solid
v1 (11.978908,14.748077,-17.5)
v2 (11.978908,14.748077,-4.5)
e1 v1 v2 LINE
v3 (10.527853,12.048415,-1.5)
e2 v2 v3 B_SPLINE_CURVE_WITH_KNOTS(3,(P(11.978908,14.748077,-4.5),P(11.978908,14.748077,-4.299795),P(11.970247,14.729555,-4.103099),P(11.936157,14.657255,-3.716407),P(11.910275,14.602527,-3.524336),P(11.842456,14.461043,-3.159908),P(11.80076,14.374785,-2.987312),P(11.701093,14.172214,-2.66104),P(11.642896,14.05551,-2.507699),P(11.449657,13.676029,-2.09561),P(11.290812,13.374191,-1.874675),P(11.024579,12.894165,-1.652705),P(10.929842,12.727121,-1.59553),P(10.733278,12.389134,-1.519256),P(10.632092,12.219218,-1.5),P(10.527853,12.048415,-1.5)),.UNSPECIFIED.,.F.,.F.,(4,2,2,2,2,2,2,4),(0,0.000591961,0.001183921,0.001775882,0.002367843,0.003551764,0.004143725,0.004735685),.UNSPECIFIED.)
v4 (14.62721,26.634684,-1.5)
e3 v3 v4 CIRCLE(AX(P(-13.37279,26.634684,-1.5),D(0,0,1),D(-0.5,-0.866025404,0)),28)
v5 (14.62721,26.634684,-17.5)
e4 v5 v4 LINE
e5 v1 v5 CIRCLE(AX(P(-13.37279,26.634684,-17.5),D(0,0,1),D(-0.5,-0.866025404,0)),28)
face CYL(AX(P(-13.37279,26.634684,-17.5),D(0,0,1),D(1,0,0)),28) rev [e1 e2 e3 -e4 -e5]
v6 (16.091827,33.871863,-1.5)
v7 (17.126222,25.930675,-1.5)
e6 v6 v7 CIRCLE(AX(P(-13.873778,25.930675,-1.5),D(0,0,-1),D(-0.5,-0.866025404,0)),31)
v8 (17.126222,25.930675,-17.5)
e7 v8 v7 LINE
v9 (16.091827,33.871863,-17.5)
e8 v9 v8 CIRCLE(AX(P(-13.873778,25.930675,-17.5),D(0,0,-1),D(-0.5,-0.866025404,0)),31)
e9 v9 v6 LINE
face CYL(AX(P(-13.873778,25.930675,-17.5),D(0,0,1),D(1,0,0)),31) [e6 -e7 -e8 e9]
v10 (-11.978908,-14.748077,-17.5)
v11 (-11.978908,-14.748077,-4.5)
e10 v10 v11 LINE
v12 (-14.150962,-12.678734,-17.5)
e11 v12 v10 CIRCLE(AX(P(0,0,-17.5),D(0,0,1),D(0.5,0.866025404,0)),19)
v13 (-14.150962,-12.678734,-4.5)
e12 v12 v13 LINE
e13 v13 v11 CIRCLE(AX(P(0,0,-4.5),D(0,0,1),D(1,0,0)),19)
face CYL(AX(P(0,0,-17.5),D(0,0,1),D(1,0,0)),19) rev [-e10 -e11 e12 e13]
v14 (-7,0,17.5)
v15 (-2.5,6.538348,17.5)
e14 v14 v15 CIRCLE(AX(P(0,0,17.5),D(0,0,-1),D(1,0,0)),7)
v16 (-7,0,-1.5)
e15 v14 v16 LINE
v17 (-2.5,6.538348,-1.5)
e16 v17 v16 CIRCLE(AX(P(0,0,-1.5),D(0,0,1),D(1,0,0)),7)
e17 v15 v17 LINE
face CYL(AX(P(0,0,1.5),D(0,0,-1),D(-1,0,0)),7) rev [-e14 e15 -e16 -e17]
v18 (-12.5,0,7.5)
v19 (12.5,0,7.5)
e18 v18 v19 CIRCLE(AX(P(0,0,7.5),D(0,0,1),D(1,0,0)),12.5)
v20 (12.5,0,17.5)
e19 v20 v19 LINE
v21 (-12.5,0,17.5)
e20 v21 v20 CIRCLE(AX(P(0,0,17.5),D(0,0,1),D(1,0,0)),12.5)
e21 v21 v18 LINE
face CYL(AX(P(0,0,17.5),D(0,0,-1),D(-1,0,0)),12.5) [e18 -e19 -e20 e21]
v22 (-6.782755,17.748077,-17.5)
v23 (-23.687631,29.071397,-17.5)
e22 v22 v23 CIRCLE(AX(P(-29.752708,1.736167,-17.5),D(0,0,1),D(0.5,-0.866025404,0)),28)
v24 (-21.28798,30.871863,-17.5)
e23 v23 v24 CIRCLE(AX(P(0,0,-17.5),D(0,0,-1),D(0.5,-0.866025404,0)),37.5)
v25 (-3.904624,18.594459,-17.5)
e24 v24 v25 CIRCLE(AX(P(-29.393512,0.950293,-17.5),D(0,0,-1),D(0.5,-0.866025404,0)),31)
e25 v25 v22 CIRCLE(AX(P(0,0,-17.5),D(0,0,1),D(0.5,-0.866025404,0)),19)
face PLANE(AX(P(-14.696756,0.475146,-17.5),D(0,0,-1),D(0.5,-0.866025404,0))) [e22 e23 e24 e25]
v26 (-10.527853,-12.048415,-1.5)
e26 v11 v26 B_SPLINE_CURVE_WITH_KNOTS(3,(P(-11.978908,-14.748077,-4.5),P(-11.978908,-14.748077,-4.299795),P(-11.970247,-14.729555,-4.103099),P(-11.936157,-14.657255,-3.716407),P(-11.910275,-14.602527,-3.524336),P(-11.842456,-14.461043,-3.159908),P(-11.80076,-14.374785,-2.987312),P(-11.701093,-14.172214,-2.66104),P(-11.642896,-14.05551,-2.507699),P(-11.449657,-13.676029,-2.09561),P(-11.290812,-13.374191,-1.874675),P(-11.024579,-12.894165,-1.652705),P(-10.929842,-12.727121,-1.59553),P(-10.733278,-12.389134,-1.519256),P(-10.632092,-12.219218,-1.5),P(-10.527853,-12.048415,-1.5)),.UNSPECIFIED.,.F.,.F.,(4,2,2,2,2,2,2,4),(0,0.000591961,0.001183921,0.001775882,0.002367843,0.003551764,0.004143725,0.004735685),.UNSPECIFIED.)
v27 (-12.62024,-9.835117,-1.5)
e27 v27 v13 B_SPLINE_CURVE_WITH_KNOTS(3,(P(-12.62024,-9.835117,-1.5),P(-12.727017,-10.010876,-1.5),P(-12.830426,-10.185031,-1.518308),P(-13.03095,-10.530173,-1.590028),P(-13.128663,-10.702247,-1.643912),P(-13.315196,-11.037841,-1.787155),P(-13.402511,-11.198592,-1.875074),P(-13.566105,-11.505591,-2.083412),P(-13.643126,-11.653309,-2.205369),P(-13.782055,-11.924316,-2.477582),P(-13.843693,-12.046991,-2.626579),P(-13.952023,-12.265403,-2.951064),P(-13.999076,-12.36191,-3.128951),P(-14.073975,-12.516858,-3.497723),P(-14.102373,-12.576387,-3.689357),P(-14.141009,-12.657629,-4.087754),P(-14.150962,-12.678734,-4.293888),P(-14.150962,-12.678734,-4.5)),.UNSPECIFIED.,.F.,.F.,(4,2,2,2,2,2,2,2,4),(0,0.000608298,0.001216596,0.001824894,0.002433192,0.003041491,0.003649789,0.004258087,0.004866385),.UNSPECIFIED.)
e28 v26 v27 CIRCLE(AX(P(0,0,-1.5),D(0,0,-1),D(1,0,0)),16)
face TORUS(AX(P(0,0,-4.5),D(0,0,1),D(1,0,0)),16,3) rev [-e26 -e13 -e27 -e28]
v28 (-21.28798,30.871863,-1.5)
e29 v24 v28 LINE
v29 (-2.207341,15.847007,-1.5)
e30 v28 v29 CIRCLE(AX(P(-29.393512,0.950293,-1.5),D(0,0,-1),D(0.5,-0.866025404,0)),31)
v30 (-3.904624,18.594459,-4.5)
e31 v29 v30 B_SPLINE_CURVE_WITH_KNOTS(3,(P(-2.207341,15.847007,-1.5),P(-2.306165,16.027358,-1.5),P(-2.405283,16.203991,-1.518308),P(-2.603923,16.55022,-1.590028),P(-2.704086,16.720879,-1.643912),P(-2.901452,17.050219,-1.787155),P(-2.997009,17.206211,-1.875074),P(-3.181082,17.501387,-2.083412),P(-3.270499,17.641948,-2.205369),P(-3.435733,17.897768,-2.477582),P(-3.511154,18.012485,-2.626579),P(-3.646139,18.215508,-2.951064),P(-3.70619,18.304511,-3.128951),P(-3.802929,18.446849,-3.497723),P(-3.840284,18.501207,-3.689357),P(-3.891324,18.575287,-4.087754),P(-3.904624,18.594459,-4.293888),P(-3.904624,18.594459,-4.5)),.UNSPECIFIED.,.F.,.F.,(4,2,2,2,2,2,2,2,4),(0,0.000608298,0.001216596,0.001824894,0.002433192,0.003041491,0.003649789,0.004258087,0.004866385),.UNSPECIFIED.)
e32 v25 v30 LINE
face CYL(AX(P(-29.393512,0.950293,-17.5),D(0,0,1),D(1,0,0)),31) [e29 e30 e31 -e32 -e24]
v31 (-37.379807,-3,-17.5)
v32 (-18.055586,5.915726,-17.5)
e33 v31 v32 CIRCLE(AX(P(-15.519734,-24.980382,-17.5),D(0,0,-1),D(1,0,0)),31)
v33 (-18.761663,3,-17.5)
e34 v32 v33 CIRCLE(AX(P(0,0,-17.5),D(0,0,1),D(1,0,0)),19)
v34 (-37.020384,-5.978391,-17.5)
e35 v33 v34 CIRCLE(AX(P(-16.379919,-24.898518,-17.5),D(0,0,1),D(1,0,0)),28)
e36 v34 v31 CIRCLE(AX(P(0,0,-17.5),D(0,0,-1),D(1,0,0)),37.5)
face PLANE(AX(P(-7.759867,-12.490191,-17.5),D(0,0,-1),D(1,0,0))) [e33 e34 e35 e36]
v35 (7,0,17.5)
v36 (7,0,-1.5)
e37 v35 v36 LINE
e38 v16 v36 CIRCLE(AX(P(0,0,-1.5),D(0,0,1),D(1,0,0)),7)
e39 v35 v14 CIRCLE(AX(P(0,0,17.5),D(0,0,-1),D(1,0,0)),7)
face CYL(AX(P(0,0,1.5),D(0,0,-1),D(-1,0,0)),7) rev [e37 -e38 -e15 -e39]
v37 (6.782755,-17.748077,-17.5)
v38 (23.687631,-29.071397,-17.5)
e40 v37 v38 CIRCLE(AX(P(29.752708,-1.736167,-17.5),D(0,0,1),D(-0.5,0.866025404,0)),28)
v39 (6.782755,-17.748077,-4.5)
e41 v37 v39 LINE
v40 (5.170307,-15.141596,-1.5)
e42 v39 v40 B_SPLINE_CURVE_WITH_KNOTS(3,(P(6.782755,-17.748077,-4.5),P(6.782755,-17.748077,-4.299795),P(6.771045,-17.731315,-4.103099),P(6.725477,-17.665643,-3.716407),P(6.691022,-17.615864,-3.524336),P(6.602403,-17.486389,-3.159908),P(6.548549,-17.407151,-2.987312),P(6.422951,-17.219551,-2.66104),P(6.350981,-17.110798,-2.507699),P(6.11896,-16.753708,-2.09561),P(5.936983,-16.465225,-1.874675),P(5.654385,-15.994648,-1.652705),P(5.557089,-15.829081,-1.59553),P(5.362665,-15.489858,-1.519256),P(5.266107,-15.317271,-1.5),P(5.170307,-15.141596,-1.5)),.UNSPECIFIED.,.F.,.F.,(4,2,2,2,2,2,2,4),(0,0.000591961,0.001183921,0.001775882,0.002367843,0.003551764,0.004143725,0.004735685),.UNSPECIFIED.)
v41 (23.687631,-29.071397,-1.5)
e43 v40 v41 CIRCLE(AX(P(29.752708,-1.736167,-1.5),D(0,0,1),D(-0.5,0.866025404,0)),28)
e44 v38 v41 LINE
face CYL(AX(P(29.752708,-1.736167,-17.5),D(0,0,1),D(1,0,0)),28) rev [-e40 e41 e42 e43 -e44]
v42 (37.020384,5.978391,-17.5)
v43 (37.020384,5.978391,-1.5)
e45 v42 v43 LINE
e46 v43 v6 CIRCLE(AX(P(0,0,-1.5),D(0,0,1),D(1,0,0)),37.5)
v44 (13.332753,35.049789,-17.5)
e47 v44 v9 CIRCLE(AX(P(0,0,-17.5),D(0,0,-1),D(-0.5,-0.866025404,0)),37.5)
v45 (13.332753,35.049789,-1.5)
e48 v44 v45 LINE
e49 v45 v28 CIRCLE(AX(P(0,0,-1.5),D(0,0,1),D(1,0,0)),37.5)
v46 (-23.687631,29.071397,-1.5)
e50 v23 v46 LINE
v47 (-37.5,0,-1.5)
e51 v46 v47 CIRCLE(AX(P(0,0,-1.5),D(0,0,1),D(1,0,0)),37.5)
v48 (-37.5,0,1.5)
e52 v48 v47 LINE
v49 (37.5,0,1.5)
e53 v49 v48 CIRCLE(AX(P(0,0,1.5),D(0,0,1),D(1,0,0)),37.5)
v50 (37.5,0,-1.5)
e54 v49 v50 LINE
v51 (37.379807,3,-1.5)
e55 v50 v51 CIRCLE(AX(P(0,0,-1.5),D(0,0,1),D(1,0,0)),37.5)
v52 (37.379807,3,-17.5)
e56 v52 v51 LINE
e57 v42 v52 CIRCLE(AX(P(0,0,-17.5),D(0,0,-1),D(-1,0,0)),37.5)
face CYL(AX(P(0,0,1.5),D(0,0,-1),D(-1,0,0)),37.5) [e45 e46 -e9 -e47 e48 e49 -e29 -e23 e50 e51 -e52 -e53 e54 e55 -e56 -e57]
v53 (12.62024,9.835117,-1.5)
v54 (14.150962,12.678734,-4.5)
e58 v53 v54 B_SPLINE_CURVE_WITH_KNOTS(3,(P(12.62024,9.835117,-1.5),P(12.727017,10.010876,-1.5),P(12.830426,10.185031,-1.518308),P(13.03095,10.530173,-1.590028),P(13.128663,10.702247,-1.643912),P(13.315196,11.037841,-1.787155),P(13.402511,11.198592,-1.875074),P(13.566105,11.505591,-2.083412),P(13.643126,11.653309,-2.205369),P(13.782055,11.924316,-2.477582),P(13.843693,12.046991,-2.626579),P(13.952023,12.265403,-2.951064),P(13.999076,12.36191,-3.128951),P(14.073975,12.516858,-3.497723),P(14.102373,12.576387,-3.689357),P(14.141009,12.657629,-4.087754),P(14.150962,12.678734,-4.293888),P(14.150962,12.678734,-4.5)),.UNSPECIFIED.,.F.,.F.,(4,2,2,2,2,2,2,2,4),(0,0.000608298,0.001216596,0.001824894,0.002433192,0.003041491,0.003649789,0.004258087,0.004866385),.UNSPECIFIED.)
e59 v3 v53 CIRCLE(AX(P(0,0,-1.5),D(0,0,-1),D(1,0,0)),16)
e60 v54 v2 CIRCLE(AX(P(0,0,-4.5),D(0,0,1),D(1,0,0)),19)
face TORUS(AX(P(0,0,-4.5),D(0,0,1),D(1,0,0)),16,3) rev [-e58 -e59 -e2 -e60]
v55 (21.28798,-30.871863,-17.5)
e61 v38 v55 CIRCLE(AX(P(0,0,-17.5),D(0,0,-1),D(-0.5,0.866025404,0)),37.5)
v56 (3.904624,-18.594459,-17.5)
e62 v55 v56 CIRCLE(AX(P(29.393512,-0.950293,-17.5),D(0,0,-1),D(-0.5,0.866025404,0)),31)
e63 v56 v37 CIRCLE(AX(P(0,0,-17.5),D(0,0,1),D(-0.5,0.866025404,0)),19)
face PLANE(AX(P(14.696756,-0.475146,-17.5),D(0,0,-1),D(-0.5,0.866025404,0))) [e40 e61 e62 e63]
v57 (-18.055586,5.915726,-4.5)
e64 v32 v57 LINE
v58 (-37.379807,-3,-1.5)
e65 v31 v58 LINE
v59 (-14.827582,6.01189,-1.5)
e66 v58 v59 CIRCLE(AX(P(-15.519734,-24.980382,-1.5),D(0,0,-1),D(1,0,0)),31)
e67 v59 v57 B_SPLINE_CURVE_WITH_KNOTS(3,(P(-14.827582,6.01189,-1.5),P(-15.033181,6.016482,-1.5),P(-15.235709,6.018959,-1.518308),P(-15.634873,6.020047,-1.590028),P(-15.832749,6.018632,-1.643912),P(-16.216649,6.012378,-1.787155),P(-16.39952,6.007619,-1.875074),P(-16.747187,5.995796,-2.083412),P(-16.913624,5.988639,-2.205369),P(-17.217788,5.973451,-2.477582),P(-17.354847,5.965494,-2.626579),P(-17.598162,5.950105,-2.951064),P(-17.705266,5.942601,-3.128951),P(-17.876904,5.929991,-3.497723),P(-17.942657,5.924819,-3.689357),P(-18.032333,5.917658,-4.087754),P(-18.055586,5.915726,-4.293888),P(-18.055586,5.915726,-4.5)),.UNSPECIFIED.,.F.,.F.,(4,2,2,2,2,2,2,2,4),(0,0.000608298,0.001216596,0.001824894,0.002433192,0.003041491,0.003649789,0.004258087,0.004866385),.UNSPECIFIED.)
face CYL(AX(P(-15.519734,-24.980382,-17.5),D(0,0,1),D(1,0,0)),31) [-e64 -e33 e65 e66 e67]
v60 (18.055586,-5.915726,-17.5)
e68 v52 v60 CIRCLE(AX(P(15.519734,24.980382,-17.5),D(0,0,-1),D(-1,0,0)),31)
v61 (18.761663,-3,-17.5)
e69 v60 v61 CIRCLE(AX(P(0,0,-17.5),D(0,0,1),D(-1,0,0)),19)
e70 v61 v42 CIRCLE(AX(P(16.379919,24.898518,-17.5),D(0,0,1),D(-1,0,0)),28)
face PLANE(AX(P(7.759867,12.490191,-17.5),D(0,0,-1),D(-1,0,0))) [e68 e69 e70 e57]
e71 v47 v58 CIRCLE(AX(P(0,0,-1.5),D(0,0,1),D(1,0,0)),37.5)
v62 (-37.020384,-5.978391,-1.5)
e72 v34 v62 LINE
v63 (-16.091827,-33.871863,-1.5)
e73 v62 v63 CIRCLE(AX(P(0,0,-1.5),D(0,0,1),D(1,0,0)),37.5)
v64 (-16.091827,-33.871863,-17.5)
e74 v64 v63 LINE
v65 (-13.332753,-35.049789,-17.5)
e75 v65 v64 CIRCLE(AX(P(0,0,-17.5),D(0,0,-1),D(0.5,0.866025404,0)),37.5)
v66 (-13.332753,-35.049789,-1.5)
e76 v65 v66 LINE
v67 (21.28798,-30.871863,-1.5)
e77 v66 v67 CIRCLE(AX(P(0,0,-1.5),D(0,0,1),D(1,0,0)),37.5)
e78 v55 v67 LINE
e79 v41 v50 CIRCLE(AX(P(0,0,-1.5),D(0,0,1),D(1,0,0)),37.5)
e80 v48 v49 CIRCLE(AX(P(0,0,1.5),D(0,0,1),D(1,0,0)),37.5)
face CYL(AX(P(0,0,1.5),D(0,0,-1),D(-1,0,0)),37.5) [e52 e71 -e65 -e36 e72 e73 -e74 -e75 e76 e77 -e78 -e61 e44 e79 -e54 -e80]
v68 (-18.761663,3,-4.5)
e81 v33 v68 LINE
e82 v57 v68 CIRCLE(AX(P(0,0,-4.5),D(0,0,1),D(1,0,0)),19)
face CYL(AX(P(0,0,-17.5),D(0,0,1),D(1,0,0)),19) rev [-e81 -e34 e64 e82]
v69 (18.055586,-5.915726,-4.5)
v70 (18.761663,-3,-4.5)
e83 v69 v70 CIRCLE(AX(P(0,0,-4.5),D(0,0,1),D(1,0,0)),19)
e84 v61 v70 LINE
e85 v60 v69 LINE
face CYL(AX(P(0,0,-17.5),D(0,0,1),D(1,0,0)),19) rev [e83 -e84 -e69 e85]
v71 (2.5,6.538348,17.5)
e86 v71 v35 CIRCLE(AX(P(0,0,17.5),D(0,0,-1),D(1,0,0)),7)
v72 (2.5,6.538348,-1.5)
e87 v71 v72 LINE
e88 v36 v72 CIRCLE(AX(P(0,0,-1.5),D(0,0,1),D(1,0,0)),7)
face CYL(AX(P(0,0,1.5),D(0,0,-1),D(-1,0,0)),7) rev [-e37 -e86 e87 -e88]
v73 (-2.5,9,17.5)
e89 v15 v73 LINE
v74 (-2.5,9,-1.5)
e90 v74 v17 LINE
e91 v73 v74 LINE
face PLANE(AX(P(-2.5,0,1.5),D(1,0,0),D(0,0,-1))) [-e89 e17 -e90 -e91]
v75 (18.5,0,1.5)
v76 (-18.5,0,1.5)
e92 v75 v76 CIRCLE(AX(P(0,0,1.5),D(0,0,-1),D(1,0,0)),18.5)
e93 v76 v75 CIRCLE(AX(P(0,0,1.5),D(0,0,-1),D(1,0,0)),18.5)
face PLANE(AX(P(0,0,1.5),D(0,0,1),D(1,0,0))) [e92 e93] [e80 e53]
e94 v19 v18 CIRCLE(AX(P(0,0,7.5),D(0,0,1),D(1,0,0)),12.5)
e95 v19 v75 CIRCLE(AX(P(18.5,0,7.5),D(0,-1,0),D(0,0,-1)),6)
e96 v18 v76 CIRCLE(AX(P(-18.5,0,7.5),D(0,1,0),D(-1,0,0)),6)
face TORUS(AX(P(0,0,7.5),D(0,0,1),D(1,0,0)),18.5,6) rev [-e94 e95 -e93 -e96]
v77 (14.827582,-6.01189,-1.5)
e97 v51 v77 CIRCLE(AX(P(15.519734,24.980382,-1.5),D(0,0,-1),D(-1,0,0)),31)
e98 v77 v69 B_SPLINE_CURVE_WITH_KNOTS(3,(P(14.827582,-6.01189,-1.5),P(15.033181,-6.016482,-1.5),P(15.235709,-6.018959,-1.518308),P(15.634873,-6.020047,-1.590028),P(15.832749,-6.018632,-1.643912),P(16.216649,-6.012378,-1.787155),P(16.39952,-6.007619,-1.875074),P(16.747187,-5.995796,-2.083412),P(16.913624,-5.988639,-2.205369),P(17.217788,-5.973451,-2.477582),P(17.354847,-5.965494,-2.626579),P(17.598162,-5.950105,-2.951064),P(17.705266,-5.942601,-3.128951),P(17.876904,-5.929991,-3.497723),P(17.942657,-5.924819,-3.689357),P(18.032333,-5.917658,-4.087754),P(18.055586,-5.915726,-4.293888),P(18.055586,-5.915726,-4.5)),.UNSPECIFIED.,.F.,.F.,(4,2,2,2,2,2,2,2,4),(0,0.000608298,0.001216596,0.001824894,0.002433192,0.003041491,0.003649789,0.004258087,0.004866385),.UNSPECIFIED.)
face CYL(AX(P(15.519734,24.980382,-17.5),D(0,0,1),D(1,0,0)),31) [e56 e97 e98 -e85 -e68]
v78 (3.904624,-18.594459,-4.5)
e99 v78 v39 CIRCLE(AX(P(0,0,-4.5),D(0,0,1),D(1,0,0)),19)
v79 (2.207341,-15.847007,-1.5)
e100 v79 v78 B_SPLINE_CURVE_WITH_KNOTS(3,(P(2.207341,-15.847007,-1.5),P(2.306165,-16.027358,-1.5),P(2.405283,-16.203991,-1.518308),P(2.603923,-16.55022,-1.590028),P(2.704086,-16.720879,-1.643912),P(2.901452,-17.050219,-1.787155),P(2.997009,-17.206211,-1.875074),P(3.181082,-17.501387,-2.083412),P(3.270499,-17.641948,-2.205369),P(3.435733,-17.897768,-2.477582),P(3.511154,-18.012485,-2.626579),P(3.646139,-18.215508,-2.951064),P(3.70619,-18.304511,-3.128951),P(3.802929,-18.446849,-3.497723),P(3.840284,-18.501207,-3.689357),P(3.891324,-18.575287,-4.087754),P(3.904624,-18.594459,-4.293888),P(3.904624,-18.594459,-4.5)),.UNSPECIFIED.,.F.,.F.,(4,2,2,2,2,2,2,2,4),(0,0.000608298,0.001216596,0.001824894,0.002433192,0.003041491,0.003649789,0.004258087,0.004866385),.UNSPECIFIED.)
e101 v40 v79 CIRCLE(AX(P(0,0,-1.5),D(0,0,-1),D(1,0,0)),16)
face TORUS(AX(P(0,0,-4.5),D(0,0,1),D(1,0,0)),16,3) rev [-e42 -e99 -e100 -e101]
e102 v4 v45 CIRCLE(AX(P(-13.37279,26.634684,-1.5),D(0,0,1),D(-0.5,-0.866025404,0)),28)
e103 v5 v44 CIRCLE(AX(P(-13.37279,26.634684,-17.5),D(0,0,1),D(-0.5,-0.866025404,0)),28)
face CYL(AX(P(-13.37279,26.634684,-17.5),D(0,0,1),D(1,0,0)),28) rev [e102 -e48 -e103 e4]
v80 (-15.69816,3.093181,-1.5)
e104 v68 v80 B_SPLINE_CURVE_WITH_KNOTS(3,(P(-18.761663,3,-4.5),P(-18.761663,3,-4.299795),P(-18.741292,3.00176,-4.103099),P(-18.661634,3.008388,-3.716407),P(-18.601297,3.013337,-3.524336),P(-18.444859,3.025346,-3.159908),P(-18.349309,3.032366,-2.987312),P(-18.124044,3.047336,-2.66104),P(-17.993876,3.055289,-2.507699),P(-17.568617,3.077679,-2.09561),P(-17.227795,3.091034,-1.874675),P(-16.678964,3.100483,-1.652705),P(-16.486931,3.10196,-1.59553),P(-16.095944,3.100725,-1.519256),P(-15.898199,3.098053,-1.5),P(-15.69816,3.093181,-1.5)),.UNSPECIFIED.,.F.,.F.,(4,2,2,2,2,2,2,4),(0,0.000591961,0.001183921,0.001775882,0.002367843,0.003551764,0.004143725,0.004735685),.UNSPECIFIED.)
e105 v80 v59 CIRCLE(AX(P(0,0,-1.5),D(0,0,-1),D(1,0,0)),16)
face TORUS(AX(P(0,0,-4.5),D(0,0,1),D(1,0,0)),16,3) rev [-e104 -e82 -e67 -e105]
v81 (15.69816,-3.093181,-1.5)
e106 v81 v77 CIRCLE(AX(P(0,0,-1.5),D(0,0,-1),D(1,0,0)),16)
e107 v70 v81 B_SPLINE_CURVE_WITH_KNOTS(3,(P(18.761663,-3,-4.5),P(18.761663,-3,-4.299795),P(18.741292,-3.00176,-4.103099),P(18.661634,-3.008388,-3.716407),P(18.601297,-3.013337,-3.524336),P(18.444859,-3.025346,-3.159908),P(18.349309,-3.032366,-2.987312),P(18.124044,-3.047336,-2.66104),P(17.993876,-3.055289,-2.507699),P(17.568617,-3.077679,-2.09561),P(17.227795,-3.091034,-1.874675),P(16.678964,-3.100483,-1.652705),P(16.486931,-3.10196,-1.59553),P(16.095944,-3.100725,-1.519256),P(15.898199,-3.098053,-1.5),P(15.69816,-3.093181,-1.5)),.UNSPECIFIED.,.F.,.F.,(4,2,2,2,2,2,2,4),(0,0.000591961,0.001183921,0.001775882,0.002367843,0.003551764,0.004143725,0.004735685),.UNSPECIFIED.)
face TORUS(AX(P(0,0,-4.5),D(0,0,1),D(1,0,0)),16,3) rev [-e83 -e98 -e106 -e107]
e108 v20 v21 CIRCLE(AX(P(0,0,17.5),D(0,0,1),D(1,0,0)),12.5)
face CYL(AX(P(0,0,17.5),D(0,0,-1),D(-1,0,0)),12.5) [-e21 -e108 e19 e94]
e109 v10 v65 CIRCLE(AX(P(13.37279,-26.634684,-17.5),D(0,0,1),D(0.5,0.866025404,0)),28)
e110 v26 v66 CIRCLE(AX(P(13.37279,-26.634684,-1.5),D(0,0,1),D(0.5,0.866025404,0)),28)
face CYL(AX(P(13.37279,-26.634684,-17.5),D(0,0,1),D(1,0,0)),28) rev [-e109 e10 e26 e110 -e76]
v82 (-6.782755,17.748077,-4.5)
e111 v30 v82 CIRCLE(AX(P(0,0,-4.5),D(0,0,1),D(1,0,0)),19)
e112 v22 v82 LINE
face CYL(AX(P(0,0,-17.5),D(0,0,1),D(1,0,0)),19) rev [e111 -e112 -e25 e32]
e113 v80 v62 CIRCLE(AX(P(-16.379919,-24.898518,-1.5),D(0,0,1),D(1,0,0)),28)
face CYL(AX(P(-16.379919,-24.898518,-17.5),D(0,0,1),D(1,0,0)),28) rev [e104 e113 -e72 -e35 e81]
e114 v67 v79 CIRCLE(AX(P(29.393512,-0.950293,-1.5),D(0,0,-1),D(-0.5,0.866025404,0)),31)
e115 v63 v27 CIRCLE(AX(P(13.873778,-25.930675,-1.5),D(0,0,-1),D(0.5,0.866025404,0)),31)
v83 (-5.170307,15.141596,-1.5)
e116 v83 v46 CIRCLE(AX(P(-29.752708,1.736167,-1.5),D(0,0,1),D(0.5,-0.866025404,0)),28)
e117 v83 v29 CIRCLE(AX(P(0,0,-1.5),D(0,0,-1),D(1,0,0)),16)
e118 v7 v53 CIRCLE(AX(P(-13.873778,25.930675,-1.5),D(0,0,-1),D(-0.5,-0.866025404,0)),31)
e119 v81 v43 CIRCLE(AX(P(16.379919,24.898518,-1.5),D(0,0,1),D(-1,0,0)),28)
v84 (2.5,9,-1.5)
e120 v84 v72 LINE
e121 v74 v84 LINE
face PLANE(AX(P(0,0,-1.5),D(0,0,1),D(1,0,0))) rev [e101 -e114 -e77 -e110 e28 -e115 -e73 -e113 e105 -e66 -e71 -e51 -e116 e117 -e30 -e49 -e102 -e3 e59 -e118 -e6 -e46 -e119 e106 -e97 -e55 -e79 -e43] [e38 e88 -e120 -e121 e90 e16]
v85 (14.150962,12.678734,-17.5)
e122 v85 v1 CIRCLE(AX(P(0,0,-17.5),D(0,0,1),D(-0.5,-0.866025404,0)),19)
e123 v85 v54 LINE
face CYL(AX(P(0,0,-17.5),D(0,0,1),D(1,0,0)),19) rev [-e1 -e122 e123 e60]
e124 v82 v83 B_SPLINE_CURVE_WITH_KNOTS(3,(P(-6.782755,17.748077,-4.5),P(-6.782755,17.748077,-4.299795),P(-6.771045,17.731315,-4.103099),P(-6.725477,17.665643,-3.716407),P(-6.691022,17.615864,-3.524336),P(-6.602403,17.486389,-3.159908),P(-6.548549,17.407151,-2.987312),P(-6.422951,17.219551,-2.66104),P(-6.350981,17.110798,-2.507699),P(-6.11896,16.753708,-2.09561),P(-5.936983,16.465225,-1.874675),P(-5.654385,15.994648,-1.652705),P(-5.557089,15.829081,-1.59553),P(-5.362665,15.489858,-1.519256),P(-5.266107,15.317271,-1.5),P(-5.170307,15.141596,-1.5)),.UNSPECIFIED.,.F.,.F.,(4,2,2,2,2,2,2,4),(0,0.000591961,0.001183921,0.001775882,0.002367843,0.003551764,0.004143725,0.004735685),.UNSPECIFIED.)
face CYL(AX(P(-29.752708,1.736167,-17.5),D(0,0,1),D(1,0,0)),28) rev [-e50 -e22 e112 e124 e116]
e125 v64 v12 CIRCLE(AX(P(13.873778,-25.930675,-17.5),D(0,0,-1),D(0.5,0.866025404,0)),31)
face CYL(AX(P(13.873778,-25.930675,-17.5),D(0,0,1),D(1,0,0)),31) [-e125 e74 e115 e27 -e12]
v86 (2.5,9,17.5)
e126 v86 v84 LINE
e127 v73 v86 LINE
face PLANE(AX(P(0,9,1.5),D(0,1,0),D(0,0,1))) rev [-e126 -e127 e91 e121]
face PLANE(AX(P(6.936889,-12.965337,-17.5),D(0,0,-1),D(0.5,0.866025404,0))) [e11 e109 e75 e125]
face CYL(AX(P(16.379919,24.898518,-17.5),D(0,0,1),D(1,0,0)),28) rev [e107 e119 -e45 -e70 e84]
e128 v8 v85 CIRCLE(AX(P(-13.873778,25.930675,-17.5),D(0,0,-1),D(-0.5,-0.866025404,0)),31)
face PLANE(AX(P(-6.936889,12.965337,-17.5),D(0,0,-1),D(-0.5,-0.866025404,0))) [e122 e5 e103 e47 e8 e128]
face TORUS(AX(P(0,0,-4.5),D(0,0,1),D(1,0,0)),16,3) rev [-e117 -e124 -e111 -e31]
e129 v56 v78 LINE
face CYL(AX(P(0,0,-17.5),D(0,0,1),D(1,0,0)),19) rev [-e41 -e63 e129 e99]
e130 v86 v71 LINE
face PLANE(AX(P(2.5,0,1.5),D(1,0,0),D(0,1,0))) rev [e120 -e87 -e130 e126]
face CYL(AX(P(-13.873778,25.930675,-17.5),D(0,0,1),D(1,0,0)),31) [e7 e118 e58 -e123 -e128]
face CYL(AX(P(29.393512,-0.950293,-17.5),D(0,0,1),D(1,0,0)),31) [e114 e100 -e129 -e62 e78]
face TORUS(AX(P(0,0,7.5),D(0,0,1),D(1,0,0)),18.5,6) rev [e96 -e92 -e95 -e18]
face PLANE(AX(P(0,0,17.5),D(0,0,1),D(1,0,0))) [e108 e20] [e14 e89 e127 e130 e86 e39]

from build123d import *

# Parameters (mm, degrees)
BACK_PLATE_PROFILE_SKETCH_R              = 37.5
BACK_PLATE_75_DEPTH                      = 1.5
HUB_START                                = 16
HUB_SKETCH_25_R                          = 12.5
HUB_25_DEPTH                             = 16
HUB_ROOT_FILLET_R6_R                     = 6
VANE_DEPTH                               = 16
VANE_ROOT_FILLET_R3_R                    = 3
VANE_PATTERN_6X_COUNT                    = 6
VANE_ROOT_FILLET_R3_OF_VANE_PATTERN_6X_R = 3


with BuildPart() as part:
    # Back Plate Profile Sketch → Back Plate Ø75 (new, symmetric)
    with BuildSketch(Plane.XY):
        Circle(BACK_PLATE_PROFILE_SKETCH_R)
        with BuildLine():
            ThreePointArc((-2.5, 6.538348415), (0, -7), (2.5, 6.538348415))
            Line((2.5, 6.538348415), (2.5, 9))
            Line((2.5, 9), (-2.5, 9))
            Line((-2.5, 9), (-2.5, 6.538348415))
        make_face(mode=Mode.SUBTRACT)
    extrude(amount=BACK_PLATE_75_DEPTH, both=True)

    # Hub Sketch Ø25 → Hub Ø25 (add)
    with BuildSketch(Plane.XY.offset(1.5).offset(HUB_START)):
        Circle(HUB_SKETCH_25_R)
        with BuildLine():
            Line((2.5, 9), (2.5, 6.538348415))
            ThreePointArc((2.5, 6.538348415), (0, -7), (-2.5, 6.538348415))
            Line((-2.5, 6.538348415), (-2.5, 9))
            Line((-2.5, 9), (2.5, 9))
        make_face(mode=Mode.SUBTRACT)
    extrude(amount=-HUB_25_DEPTH)

    # Hub Root Fillet R6
    hub_root_fillet_r6_edges = [part.edges().sort_by_distance(p)[0] for p in [
        (-12.5, 0, 1.5),
    ]]
    fillet(hub_root_fillet_r6_edges, radius=HUB_ROOT_FILLET_R6_R)

    # Vane Profile Sketch → Vane (add)
    with BuildSketch(Plane(origin=(0, 0, -1.5), x_dir=(-1, 0, 0), z_dir=(0, 0, -1))):
        with BuildLine():
            ThreePointArc((-37.020384076, 5.978391325), (-28.735420007, -0.227993827), (-18.761663039, -3))
            ThreePointArc((-18.761663039, -3), (-18.46626176, -4.471820281), (-18.055586153, -5.915725541))
            ThreePointArc((-18.055586153, -5.915725541), (-28.50675968, -3.168102302), (-37.379807383, 3))
            ThreePointArc((-37.379807383, 3), (-37.229891566, 4.492791335), (-37.020384076, 5.978391325))
        make_face()
    vane = extrude(amount=VANE_DEPTH)

    # Vane Root Fillet R3
    vane_root_fillet_r3_edges = [part.edges().sort_by_distance(p)[0] for p in [
        (18.46626176, -4.471820281, -1.5),
    ]]
    fillet(vane_root_fillet_r3_edges, radius=VANE_ROOT_FILLET_R3_R)

    # Vane Pattern 6x: Vane ×6 about axis
    vane_pattern_6x_axis = Axis((0, 0, 0), (0, 0, 1))
    for i in range(1, VANE_PATTERN_6X_COUNT):
        add(vane.rotate(vane_pattern_6x_axis, i * 360 / VANE_PATTERN_6X_COUNT))

    # Vane Root Fillet R3 of Vane Pattern 6x
    vane_root_fillet_r3_of_vane_pattern_6x_edges = [part.edges().sort_by_distance(p)[0] for p in [
        (13.105840844, 13.756341656, -1.5),
        (-5.360420916, 18.228161937, -1.5),
        (-18.46626176, 4.471820281, -1.5),
        (-13.105840844, -13.756341656, -1.5),
        (5.360420916, -18.228161937, -1.5),
    ]]
    fillet(vane_root_fillet_r3_of_vane_pattern_6x_edges, radius=VANE_ROOT_FILLET_R3_OF_VANE_PATTERN_6X_R)


solid = part.part
